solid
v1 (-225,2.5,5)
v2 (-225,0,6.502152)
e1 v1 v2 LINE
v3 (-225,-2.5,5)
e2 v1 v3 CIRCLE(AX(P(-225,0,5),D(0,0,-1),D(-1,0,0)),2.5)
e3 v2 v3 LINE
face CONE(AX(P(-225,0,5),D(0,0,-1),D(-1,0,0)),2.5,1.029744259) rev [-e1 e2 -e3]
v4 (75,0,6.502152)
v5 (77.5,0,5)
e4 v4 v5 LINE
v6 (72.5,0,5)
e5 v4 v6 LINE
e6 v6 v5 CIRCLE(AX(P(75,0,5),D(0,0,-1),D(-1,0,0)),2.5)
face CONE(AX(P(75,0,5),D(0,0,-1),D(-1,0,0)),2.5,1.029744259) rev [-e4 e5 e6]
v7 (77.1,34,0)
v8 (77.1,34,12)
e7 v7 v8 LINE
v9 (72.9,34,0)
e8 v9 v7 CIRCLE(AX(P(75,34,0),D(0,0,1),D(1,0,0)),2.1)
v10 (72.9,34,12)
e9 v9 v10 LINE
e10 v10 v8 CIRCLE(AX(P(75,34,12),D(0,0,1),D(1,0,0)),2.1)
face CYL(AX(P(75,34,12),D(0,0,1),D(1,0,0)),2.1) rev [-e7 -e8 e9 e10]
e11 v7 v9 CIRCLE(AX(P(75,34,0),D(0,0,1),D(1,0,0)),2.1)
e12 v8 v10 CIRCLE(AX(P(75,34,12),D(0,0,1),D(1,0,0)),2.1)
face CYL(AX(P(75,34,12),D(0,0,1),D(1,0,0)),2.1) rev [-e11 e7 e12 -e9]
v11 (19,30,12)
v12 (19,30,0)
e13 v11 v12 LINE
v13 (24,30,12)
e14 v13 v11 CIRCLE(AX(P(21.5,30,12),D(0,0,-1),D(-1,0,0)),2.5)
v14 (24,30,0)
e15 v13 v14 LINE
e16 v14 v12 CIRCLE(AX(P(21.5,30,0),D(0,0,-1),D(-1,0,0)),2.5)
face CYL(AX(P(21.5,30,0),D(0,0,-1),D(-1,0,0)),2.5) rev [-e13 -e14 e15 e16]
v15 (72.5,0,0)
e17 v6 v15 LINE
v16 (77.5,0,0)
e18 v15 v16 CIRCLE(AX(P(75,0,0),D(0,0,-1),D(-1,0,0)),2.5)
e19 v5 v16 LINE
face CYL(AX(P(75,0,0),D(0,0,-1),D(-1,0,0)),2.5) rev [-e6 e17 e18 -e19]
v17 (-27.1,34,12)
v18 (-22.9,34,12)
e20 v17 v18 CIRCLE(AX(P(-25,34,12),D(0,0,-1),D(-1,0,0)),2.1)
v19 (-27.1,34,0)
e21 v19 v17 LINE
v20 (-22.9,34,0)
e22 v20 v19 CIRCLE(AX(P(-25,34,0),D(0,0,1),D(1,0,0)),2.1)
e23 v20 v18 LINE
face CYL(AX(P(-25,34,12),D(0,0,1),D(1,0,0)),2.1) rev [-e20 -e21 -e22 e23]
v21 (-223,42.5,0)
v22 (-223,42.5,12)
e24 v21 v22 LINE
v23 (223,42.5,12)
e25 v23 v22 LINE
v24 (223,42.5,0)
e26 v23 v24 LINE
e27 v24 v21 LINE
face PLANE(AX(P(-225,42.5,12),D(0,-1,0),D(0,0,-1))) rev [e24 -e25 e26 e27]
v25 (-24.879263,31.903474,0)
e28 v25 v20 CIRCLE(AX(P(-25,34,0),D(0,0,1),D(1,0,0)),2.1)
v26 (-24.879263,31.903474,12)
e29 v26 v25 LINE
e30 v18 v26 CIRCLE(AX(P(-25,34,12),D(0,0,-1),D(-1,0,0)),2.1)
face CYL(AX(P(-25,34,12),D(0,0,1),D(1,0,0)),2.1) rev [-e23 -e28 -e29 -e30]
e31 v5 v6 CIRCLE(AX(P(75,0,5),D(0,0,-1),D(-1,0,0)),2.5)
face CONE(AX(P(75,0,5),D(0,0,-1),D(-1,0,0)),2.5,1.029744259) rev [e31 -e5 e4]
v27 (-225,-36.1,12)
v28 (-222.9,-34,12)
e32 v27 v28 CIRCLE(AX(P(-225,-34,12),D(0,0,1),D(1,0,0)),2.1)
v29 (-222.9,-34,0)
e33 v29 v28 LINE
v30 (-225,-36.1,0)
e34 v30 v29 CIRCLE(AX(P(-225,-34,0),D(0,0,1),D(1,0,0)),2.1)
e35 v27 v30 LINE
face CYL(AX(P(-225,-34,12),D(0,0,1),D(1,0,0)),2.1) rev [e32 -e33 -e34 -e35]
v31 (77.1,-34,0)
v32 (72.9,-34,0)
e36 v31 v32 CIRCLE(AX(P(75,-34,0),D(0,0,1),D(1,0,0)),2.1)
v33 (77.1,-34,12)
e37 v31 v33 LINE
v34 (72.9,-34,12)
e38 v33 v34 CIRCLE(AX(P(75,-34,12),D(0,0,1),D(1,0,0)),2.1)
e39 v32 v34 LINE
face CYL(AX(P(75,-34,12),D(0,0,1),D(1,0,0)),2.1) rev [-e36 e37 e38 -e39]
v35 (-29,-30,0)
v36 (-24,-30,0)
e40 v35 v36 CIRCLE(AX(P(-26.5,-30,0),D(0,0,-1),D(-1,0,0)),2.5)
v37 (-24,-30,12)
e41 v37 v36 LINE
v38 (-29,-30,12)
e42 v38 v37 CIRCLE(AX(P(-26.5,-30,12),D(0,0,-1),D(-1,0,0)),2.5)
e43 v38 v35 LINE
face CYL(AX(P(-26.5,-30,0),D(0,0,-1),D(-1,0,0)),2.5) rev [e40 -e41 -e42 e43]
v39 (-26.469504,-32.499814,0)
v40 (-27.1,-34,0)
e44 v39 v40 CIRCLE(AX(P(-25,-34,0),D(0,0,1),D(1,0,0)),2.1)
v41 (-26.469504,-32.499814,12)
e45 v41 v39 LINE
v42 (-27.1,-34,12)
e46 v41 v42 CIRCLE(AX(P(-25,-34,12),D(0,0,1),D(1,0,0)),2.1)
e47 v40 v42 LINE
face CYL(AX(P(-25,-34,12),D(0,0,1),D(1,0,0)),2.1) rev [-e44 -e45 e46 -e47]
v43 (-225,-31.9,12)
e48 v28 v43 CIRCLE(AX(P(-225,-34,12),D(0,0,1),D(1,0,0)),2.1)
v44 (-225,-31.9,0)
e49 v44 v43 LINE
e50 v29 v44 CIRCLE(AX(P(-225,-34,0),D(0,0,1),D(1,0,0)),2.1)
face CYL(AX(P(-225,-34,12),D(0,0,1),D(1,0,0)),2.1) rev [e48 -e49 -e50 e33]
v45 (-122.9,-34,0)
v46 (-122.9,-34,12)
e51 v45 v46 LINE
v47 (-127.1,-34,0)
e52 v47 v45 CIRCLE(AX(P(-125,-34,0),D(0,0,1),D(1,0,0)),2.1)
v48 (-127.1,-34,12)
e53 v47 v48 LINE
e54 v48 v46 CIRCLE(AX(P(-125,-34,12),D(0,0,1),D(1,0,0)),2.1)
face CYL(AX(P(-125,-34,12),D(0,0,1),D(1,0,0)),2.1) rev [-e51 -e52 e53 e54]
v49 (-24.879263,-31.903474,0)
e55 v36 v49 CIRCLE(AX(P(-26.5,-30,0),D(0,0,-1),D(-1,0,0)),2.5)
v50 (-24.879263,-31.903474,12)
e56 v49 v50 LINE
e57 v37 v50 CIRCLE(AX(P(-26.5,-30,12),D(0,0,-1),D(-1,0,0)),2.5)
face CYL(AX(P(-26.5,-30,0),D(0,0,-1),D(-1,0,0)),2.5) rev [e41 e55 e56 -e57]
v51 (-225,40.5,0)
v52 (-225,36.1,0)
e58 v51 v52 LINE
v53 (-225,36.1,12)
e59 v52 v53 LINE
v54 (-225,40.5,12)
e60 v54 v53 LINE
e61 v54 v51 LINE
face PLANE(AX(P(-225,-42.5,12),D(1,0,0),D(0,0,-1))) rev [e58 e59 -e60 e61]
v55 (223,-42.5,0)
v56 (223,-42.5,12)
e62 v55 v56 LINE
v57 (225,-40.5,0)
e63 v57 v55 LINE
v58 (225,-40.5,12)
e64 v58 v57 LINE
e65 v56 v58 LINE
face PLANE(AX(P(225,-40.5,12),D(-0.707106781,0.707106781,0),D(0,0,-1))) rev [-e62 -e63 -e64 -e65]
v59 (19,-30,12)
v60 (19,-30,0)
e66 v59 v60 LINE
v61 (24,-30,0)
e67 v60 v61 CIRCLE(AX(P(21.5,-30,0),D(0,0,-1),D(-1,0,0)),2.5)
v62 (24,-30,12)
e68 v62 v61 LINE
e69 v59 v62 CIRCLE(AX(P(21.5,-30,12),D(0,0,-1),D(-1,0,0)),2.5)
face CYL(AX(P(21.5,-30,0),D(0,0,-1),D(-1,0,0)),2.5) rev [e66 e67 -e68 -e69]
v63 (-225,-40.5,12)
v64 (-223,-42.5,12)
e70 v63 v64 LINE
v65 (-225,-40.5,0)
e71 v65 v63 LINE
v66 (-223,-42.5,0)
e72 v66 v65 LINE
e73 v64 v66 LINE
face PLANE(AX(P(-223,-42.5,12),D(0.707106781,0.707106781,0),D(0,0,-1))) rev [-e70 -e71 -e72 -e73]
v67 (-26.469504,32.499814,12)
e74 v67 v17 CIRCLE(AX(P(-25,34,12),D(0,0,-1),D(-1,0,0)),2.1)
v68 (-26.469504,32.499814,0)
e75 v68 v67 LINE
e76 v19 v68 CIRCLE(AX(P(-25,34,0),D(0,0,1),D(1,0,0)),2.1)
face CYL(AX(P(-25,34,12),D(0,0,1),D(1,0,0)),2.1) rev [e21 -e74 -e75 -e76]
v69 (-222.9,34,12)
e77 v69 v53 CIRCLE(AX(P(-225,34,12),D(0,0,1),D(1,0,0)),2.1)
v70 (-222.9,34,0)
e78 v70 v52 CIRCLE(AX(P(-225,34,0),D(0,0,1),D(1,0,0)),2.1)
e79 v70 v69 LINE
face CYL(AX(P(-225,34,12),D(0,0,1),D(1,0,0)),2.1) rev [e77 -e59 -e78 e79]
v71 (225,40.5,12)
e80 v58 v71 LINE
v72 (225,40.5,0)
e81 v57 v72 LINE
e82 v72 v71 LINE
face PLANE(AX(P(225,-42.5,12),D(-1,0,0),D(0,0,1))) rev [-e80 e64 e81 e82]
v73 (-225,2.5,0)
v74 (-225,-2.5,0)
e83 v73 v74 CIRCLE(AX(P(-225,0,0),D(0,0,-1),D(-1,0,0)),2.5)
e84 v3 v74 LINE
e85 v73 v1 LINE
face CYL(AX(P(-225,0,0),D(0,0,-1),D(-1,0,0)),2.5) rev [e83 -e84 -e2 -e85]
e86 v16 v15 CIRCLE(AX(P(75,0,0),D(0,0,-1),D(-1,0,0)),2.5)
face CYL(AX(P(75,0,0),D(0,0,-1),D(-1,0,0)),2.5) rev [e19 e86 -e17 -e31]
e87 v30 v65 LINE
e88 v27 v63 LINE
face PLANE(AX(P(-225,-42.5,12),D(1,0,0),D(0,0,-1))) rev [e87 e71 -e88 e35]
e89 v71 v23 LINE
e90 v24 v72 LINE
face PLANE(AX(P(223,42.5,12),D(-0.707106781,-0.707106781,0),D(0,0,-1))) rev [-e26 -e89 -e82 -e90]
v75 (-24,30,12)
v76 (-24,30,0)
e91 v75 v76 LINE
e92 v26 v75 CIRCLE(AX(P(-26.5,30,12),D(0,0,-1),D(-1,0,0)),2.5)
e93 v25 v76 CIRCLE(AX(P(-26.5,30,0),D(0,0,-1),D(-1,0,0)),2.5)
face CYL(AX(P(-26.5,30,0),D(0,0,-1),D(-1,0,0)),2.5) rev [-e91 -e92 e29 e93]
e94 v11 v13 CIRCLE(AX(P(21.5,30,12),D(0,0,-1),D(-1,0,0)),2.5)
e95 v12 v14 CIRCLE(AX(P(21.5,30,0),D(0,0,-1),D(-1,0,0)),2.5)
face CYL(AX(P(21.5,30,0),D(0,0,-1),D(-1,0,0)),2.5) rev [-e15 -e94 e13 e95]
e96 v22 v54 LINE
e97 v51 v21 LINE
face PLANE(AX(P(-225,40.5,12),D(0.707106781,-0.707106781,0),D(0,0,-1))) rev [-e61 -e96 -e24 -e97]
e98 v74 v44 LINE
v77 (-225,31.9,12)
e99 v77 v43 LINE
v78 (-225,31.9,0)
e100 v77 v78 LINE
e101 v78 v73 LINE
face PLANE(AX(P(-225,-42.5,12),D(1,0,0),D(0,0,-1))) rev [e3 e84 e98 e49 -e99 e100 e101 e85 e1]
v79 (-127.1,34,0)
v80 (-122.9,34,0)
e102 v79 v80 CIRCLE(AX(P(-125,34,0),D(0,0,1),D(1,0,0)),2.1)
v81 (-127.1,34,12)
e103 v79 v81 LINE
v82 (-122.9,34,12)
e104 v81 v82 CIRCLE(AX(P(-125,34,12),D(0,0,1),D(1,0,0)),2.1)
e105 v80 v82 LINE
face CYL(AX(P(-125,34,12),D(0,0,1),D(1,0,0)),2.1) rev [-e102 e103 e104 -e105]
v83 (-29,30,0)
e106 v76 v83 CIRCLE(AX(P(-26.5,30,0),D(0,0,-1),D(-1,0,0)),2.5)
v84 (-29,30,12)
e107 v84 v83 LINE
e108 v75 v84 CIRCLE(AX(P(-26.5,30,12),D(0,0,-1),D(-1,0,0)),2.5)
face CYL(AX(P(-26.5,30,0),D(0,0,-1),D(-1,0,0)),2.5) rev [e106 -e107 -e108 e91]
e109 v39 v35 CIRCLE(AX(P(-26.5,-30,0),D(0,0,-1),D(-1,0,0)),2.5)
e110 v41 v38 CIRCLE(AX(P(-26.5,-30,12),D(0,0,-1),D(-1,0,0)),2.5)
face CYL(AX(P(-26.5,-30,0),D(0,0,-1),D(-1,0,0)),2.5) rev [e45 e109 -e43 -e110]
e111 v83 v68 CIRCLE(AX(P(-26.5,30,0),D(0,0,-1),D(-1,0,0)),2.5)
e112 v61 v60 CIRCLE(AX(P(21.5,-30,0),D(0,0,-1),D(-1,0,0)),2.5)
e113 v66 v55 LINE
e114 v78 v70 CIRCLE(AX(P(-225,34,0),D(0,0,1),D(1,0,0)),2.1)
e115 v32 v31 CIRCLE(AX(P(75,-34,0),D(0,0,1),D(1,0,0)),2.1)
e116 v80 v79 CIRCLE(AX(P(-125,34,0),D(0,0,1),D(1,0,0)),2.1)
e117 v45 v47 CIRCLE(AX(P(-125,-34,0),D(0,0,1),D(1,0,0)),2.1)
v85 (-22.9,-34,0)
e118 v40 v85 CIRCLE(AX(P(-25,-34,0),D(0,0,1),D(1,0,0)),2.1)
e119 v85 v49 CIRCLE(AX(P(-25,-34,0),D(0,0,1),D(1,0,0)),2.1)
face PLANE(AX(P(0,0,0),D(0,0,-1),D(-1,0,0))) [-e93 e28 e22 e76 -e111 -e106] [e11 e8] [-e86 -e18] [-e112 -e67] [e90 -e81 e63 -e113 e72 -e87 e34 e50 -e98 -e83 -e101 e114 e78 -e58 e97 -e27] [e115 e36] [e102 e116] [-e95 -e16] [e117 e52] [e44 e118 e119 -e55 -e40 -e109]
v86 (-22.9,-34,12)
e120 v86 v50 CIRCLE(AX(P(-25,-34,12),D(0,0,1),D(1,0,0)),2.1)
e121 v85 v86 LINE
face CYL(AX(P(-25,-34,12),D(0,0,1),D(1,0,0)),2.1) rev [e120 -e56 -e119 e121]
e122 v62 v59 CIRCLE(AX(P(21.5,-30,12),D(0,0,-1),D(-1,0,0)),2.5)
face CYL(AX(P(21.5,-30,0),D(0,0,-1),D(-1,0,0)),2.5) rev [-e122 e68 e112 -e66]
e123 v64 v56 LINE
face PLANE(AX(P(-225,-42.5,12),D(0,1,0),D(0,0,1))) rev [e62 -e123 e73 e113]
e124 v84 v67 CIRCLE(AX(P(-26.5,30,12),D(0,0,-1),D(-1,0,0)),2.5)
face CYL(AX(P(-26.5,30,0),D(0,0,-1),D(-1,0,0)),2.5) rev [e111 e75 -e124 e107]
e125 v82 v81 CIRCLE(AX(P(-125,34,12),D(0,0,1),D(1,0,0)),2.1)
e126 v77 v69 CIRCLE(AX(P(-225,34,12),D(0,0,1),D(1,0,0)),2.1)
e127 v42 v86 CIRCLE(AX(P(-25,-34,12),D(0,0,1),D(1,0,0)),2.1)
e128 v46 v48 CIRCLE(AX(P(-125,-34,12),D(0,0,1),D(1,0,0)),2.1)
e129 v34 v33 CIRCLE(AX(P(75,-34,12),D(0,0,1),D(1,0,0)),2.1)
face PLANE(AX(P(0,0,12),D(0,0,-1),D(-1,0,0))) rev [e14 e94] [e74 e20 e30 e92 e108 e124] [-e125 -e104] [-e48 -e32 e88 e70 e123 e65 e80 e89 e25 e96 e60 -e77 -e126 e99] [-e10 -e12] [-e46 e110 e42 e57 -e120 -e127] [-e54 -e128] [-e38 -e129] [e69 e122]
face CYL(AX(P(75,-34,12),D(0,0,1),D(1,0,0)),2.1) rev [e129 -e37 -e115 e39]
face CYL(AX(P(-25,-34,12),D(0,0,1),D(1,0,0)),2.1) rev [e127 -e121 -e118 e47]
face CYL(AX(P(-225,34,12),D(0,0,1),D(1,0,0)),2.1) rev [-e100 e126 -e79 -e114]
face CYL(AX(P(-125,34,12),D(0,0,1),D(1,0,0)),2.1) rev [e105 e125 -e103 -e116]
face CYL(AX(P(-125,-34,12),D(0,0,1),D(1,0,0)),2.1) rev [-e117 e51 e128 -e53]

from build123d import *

# Parameters (mm, degrees)
SKETCH_1_W         = 450
SKETCH_1_H         = 85
EXTRUDE_1_DEPTH    = 12
HOLE_WIZARD_M6_1_D = 5
HOLE_WIZARD_M5_1_D = 4.2
F_5_0MM_1_D        = 5
F_5_0MM_1_DEPTH    = 5
F_5_0MM_1_TIP      = 1.502151548
CHAMFER_1_SIZE     = 2


with BuildPart() as part:
    # 草图1 → 凸台-拉伸1 (new body)
    with BuildSketch(Plane.XY):
        Rectangle(SKETCH_1_W, SKETCH_1_H)
    extrude(amount=EXTRUDE_1_DEPTH)

    # M6 螺纹孔1 (through all)
    with Locations(Plane(origin=(0, 0, 0), x_dir=(-1, 0, 0), z_dir=(0, 0, -1))):
        with Locations((26.5, 30), (-21.5, -30), (-21.5, 30), (26.5, -30), (-253.5, 30), (-301.5, -30), (-301.5, 30), (-253.5, -30)):
            Hole(HOLE_WIZARD_M6_1_D / 2)

    # M5 螺纹孔1 (through all)
    with Locations(Plane.XY.offset(12)):
        with Locations((75, 34), (75, -34), (-25, 34), (-25, -34), (-125, 34), (-125, -34), (-225, 34), (-225, -34)):
            Hole(HOLE_WIZARD_M5_1_D / 2)

    # Ø5.0mm 暗销孔1
    with Locations(Plane(origin=(0, 0, 0), x_dir=(-1, 0, 0), z_dir=(0, 0, -1))):
        with Locations((-75, 0), (225, 0)):
            Hole(F_5_0MM_1_D / 2, depth=F_5_0MM_1_DEPTH)
            with Locations((0, 0, -(F_5_0MM_1_DEPTH + F_5_0MM_1_TIP / 2))):  # 118° drill point
                Cone(0, F_5_0MM_1_D / 2, F_5_0MM_1_TIP, mode=Mode.SUBTRACT)

    # 倒角1
    chamfer_1_edges = [part.edges().sort_by_distance(p)[0] for p in [
        (225, -42.5, 6),
        (-225, -42.5, 6),
        (-225, 42.5, 6),
        (225, 42.5, 6),
    ]]
    chamfer(chamfer_1_edges, length=CHAMFER_1_SIZE)


solid = part.part
